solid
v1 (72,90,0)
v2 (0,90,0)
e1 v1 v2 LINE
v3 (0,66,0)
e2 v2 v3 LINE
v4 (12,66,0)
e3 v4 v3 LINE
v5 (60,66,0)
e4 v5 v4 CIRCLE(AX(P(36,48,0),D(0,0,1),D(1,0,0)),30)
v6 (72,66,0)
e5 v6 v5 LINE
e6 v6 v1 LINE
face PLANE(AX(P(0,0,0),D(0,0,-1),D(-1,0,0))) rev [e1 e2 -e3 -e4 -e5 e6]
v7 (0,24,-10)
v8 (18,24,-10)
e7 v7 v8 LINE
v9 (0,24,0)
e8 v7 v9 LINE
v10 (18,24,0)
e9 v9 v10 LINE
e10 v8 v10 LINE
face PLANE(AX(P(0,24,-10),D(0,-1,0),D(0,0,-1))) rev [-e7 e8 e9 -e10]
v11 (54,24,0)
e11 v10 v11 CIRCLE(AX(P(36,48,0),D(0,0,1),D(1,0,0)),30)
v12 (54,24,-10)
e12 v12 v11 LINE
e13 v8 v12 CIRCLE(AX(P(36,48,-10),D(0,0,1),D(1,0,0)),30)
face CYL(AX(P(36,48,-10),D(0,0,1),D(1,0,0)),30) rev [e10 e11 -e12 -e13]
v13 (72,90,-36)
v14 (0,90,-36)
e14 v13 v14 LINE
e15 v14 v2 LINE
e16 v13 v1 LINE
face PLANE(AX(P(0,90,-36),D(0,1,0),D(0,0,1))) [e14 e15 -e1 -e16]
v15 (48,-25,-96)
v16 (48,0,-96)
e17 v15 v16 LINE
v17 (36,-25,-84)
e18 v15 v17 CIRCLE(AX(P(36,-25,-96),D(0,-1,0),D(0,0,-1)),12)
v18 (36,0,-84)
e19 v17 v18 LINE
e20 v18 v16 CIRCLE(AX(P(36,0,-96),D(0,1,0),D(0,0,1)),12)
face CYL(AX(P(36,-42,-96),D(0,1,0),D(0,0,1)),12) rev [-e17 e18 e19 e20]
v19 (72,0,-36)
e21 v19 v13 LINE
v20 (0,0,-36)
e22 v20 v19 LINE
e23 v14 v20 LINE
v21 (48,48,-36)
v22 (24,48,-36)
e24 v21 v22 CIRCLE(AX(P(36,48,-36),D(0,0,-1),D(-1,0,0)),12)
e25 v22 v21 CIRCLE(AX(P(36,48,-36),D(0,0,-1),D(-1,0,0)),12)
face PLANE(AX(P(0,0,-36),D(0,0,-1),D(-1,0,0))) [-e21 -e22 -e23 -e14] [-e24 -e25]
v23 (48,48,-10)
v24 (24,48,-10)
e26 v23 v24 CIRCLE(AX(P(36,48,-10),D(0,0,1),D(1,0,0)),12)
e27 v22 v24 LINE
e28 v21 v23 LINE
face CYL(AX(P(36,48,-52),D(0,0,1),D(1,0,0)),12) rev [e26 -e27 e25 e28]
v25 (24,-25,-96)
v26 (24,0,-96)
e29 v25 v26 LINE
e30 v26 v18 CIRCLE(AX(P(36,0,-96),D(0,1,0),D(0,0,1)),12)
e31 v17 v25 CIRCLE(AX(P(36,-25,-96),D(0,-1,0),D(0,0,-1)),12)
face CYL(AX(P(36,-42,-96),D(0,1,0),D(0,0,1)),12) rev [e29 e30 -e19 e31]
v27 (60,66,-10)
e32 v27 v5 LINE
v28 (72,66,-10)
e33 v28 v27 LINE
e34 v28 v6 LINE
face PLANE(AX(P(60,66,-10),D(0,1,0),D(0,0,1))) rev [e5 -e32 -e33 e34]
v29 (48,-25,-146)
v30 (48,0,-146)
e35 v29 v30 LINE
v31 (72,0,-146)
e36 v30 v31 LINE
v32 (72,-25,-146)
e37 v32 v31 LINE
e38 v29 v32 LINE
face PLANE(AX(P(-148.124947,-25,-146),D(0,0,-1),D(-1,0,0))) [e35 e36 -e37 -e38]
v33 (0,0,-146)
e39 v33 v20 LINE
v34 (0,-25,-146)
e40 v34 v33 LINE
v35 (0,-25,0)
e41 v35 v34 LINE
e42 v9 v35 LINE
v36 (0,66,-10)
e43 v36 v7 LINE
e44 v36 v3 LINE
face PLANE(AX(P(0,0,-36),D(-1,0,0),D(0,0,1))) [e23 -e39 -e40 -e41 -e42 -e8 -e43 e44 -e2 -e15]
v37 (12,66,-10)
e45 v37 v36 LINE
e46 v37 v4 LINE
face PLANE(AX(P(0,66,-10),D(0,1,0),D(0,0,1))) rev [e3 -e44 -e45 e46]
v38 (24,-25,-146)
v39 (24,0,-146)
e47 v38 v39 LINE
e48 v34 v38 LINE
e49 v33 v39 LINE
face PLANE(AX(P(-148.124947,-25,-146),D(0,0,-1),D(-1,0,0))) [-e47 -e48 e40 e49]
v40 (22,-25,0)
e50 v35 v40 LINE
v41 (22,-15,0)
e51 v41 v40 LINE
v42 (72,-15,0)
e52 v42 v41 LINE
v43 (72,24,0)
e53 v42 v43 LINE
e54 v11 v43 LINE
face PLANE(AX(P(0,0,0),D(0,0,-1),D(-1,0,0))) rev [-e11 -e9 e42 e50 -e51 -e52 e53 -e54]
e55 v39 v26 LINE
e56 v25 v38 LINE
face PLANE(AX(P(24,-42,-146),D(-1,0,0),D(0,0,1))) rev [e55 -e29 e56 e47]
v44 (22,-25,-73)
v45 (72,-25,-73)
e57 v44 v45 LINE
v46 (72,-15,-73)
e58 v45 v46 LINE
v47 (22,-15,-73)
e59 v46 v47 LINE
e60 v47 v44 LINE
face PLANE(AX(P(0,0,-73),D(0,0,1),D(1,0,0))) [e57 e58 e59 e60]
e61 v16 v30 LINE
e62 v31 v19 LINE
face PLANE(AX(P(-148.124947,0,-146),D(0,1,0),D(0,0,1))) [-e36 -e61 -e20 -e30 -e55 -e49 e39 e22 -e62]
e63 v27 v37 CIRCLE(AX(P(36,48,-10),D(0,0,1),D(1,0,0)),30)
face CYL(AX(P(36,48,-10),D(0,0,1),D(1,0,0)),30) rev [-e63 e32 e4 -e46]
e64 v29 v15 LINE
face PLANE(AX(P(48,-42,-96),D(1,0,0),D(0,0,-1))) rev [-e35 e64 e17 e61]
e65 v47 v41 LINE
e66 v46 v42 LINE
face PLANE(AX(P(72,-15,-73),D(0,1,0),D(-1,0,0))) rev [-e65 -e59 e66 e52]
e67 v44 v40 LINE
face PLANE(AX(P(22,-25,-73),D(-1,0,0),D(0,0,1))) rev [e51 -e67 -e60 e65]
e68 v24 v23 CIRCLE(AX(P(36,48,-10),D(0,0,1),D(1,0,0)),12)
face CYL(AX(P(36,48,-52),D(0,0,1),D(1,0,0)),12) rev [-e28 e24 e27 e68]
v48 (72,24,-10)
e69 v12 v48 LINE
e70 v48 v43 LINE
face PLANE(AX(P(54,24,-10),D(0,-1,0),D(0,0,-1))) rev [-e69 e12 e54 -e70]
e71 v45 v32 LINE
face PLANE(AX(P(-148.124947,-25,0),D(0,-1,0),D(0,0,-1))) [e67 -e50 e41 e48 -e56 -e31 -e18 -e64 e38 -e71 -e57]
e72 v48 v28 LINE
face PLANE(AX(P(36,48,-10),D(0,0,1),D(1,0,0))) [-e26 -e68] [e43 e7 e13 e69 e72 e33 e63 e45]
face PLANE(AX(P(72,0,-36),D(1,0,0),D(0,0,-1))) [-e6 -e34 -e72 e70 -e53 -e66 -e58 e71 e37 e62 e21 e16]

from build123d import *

# Parameters (mm, degrees)
UPRIGHT_BLOCK_PROFILE_W             = 72
UPRIGHT_BLOCK_PROFILE_H             = 90
UPRIGHT_BLOCK_DEPTH                 = 36
SIDE_RECESS_10_DEEP_DEPTH           = 10
BORE_SKETCH_R                       = 12
BORE_24_DEPTH                       = 42
BASE_ARM_SKETCH_W                   = 146
BASE_ARM_SKETCH_H                   = 25
BASE_ARM_146X25_DEPTH               = 72
ARM_SLOT_DEPTH                      = 42
RELIEF_GROOVE_SKETCH_W              = 50
RELIEF_GROOVE_SKETCH_H              = 10
UNDERSIDE_RELIEF_GROOVE_10X50_DEPTH = 73


with BuildPart() as part:
    # Upright Block Profile → Upright Block (new body)
    with BuildSketch(Plane.XY):
        with Locations((36, 45)):
            Rectangle(UPRIGHT_BLOCK_PROFILE_W, UPRIGHT_BLOCK_PROFILE_H)
    extrude(amount=-UPRIGHT_BLOCK_DEPTH)

    # Side Recess Sketch → Side Recess 10 Deep (cut)
    with BuildSketch(Plane.XY):
        with BuildLine():
            Line((0, 66), (12, 66))
            ThreePointArc((12, 66), (36, 78), (60, 66))
            Line((60, 66), (72, 66))
            Line((72, 66), (72, 24))
            Line((72, 24), (54, 24))
            ThreePointArc((54, 24), (36, 18), (18, 24))
            Line((18, 24), (0, 24))
            Line((0, 24), (0, 66))
        make_face()
    extrude(amount=-SIDE_RECESS_10_DEEP_DEPTH, mode=Mode.SUBTRACT)

    # Bore Sketch → Bore Ø24 (cut)
    with BuildSketch(Plane.XY.offset(-10)):
        with Locations((36, 48)):
            Circle(BORE_SKETCH_R)
    extrude(amount=-BORE_24_DEPTH, mode=Mode.SUBTRACT)

    # Base Arm Sketch → Base Arm 146x25 (add)
    with BuildSketch(Plane(origin=(72, 0, 0), x_dir=(0, 0, -1), z_dir=(1, 0, 0))):
        with Locations((73, -12.5)):
            Rectangle(BASE_ARM_SKETCH_W, BASE_ARM_SKETCH_H)
    extrude(amount=-BASE_ARM_146X25_DEPTH)

    # Arm Slot Sketch → Arm Slot (cut)
    with BuildSketch(Plane(origin=(0, 0, 0), x_dir=(1, 0, 0), z_dir=(0, 1, 0))):
        with BuildLine():
            Line((24, 146), (24, 96))
            ThreePointArc((24, 96), (36, 84), (48, 96))
            Line((48, 96), (48, 146))
            Line((48, 146), (24, 146))
        make_face()
    extrude(amount=-ARM_SLOT_DEPTH, mode=Mode.SUBTRACT)

    # Relief Groove Sketch → Underside Relief Groove 10x50 (cut)
    with BuildSketch(Plane.XY):
        with Locations((47, -20)):
            Rectangle(RELIEF_GROOVE_SKETCH_W, RELIEF_GROOVE_SKETCH_H)
    extrude(amount=-UNDERSIDE_RELIEF_GROOVE_10X50_DEPTH, mode=Mode.SUBTRACT)


solid = part.part
